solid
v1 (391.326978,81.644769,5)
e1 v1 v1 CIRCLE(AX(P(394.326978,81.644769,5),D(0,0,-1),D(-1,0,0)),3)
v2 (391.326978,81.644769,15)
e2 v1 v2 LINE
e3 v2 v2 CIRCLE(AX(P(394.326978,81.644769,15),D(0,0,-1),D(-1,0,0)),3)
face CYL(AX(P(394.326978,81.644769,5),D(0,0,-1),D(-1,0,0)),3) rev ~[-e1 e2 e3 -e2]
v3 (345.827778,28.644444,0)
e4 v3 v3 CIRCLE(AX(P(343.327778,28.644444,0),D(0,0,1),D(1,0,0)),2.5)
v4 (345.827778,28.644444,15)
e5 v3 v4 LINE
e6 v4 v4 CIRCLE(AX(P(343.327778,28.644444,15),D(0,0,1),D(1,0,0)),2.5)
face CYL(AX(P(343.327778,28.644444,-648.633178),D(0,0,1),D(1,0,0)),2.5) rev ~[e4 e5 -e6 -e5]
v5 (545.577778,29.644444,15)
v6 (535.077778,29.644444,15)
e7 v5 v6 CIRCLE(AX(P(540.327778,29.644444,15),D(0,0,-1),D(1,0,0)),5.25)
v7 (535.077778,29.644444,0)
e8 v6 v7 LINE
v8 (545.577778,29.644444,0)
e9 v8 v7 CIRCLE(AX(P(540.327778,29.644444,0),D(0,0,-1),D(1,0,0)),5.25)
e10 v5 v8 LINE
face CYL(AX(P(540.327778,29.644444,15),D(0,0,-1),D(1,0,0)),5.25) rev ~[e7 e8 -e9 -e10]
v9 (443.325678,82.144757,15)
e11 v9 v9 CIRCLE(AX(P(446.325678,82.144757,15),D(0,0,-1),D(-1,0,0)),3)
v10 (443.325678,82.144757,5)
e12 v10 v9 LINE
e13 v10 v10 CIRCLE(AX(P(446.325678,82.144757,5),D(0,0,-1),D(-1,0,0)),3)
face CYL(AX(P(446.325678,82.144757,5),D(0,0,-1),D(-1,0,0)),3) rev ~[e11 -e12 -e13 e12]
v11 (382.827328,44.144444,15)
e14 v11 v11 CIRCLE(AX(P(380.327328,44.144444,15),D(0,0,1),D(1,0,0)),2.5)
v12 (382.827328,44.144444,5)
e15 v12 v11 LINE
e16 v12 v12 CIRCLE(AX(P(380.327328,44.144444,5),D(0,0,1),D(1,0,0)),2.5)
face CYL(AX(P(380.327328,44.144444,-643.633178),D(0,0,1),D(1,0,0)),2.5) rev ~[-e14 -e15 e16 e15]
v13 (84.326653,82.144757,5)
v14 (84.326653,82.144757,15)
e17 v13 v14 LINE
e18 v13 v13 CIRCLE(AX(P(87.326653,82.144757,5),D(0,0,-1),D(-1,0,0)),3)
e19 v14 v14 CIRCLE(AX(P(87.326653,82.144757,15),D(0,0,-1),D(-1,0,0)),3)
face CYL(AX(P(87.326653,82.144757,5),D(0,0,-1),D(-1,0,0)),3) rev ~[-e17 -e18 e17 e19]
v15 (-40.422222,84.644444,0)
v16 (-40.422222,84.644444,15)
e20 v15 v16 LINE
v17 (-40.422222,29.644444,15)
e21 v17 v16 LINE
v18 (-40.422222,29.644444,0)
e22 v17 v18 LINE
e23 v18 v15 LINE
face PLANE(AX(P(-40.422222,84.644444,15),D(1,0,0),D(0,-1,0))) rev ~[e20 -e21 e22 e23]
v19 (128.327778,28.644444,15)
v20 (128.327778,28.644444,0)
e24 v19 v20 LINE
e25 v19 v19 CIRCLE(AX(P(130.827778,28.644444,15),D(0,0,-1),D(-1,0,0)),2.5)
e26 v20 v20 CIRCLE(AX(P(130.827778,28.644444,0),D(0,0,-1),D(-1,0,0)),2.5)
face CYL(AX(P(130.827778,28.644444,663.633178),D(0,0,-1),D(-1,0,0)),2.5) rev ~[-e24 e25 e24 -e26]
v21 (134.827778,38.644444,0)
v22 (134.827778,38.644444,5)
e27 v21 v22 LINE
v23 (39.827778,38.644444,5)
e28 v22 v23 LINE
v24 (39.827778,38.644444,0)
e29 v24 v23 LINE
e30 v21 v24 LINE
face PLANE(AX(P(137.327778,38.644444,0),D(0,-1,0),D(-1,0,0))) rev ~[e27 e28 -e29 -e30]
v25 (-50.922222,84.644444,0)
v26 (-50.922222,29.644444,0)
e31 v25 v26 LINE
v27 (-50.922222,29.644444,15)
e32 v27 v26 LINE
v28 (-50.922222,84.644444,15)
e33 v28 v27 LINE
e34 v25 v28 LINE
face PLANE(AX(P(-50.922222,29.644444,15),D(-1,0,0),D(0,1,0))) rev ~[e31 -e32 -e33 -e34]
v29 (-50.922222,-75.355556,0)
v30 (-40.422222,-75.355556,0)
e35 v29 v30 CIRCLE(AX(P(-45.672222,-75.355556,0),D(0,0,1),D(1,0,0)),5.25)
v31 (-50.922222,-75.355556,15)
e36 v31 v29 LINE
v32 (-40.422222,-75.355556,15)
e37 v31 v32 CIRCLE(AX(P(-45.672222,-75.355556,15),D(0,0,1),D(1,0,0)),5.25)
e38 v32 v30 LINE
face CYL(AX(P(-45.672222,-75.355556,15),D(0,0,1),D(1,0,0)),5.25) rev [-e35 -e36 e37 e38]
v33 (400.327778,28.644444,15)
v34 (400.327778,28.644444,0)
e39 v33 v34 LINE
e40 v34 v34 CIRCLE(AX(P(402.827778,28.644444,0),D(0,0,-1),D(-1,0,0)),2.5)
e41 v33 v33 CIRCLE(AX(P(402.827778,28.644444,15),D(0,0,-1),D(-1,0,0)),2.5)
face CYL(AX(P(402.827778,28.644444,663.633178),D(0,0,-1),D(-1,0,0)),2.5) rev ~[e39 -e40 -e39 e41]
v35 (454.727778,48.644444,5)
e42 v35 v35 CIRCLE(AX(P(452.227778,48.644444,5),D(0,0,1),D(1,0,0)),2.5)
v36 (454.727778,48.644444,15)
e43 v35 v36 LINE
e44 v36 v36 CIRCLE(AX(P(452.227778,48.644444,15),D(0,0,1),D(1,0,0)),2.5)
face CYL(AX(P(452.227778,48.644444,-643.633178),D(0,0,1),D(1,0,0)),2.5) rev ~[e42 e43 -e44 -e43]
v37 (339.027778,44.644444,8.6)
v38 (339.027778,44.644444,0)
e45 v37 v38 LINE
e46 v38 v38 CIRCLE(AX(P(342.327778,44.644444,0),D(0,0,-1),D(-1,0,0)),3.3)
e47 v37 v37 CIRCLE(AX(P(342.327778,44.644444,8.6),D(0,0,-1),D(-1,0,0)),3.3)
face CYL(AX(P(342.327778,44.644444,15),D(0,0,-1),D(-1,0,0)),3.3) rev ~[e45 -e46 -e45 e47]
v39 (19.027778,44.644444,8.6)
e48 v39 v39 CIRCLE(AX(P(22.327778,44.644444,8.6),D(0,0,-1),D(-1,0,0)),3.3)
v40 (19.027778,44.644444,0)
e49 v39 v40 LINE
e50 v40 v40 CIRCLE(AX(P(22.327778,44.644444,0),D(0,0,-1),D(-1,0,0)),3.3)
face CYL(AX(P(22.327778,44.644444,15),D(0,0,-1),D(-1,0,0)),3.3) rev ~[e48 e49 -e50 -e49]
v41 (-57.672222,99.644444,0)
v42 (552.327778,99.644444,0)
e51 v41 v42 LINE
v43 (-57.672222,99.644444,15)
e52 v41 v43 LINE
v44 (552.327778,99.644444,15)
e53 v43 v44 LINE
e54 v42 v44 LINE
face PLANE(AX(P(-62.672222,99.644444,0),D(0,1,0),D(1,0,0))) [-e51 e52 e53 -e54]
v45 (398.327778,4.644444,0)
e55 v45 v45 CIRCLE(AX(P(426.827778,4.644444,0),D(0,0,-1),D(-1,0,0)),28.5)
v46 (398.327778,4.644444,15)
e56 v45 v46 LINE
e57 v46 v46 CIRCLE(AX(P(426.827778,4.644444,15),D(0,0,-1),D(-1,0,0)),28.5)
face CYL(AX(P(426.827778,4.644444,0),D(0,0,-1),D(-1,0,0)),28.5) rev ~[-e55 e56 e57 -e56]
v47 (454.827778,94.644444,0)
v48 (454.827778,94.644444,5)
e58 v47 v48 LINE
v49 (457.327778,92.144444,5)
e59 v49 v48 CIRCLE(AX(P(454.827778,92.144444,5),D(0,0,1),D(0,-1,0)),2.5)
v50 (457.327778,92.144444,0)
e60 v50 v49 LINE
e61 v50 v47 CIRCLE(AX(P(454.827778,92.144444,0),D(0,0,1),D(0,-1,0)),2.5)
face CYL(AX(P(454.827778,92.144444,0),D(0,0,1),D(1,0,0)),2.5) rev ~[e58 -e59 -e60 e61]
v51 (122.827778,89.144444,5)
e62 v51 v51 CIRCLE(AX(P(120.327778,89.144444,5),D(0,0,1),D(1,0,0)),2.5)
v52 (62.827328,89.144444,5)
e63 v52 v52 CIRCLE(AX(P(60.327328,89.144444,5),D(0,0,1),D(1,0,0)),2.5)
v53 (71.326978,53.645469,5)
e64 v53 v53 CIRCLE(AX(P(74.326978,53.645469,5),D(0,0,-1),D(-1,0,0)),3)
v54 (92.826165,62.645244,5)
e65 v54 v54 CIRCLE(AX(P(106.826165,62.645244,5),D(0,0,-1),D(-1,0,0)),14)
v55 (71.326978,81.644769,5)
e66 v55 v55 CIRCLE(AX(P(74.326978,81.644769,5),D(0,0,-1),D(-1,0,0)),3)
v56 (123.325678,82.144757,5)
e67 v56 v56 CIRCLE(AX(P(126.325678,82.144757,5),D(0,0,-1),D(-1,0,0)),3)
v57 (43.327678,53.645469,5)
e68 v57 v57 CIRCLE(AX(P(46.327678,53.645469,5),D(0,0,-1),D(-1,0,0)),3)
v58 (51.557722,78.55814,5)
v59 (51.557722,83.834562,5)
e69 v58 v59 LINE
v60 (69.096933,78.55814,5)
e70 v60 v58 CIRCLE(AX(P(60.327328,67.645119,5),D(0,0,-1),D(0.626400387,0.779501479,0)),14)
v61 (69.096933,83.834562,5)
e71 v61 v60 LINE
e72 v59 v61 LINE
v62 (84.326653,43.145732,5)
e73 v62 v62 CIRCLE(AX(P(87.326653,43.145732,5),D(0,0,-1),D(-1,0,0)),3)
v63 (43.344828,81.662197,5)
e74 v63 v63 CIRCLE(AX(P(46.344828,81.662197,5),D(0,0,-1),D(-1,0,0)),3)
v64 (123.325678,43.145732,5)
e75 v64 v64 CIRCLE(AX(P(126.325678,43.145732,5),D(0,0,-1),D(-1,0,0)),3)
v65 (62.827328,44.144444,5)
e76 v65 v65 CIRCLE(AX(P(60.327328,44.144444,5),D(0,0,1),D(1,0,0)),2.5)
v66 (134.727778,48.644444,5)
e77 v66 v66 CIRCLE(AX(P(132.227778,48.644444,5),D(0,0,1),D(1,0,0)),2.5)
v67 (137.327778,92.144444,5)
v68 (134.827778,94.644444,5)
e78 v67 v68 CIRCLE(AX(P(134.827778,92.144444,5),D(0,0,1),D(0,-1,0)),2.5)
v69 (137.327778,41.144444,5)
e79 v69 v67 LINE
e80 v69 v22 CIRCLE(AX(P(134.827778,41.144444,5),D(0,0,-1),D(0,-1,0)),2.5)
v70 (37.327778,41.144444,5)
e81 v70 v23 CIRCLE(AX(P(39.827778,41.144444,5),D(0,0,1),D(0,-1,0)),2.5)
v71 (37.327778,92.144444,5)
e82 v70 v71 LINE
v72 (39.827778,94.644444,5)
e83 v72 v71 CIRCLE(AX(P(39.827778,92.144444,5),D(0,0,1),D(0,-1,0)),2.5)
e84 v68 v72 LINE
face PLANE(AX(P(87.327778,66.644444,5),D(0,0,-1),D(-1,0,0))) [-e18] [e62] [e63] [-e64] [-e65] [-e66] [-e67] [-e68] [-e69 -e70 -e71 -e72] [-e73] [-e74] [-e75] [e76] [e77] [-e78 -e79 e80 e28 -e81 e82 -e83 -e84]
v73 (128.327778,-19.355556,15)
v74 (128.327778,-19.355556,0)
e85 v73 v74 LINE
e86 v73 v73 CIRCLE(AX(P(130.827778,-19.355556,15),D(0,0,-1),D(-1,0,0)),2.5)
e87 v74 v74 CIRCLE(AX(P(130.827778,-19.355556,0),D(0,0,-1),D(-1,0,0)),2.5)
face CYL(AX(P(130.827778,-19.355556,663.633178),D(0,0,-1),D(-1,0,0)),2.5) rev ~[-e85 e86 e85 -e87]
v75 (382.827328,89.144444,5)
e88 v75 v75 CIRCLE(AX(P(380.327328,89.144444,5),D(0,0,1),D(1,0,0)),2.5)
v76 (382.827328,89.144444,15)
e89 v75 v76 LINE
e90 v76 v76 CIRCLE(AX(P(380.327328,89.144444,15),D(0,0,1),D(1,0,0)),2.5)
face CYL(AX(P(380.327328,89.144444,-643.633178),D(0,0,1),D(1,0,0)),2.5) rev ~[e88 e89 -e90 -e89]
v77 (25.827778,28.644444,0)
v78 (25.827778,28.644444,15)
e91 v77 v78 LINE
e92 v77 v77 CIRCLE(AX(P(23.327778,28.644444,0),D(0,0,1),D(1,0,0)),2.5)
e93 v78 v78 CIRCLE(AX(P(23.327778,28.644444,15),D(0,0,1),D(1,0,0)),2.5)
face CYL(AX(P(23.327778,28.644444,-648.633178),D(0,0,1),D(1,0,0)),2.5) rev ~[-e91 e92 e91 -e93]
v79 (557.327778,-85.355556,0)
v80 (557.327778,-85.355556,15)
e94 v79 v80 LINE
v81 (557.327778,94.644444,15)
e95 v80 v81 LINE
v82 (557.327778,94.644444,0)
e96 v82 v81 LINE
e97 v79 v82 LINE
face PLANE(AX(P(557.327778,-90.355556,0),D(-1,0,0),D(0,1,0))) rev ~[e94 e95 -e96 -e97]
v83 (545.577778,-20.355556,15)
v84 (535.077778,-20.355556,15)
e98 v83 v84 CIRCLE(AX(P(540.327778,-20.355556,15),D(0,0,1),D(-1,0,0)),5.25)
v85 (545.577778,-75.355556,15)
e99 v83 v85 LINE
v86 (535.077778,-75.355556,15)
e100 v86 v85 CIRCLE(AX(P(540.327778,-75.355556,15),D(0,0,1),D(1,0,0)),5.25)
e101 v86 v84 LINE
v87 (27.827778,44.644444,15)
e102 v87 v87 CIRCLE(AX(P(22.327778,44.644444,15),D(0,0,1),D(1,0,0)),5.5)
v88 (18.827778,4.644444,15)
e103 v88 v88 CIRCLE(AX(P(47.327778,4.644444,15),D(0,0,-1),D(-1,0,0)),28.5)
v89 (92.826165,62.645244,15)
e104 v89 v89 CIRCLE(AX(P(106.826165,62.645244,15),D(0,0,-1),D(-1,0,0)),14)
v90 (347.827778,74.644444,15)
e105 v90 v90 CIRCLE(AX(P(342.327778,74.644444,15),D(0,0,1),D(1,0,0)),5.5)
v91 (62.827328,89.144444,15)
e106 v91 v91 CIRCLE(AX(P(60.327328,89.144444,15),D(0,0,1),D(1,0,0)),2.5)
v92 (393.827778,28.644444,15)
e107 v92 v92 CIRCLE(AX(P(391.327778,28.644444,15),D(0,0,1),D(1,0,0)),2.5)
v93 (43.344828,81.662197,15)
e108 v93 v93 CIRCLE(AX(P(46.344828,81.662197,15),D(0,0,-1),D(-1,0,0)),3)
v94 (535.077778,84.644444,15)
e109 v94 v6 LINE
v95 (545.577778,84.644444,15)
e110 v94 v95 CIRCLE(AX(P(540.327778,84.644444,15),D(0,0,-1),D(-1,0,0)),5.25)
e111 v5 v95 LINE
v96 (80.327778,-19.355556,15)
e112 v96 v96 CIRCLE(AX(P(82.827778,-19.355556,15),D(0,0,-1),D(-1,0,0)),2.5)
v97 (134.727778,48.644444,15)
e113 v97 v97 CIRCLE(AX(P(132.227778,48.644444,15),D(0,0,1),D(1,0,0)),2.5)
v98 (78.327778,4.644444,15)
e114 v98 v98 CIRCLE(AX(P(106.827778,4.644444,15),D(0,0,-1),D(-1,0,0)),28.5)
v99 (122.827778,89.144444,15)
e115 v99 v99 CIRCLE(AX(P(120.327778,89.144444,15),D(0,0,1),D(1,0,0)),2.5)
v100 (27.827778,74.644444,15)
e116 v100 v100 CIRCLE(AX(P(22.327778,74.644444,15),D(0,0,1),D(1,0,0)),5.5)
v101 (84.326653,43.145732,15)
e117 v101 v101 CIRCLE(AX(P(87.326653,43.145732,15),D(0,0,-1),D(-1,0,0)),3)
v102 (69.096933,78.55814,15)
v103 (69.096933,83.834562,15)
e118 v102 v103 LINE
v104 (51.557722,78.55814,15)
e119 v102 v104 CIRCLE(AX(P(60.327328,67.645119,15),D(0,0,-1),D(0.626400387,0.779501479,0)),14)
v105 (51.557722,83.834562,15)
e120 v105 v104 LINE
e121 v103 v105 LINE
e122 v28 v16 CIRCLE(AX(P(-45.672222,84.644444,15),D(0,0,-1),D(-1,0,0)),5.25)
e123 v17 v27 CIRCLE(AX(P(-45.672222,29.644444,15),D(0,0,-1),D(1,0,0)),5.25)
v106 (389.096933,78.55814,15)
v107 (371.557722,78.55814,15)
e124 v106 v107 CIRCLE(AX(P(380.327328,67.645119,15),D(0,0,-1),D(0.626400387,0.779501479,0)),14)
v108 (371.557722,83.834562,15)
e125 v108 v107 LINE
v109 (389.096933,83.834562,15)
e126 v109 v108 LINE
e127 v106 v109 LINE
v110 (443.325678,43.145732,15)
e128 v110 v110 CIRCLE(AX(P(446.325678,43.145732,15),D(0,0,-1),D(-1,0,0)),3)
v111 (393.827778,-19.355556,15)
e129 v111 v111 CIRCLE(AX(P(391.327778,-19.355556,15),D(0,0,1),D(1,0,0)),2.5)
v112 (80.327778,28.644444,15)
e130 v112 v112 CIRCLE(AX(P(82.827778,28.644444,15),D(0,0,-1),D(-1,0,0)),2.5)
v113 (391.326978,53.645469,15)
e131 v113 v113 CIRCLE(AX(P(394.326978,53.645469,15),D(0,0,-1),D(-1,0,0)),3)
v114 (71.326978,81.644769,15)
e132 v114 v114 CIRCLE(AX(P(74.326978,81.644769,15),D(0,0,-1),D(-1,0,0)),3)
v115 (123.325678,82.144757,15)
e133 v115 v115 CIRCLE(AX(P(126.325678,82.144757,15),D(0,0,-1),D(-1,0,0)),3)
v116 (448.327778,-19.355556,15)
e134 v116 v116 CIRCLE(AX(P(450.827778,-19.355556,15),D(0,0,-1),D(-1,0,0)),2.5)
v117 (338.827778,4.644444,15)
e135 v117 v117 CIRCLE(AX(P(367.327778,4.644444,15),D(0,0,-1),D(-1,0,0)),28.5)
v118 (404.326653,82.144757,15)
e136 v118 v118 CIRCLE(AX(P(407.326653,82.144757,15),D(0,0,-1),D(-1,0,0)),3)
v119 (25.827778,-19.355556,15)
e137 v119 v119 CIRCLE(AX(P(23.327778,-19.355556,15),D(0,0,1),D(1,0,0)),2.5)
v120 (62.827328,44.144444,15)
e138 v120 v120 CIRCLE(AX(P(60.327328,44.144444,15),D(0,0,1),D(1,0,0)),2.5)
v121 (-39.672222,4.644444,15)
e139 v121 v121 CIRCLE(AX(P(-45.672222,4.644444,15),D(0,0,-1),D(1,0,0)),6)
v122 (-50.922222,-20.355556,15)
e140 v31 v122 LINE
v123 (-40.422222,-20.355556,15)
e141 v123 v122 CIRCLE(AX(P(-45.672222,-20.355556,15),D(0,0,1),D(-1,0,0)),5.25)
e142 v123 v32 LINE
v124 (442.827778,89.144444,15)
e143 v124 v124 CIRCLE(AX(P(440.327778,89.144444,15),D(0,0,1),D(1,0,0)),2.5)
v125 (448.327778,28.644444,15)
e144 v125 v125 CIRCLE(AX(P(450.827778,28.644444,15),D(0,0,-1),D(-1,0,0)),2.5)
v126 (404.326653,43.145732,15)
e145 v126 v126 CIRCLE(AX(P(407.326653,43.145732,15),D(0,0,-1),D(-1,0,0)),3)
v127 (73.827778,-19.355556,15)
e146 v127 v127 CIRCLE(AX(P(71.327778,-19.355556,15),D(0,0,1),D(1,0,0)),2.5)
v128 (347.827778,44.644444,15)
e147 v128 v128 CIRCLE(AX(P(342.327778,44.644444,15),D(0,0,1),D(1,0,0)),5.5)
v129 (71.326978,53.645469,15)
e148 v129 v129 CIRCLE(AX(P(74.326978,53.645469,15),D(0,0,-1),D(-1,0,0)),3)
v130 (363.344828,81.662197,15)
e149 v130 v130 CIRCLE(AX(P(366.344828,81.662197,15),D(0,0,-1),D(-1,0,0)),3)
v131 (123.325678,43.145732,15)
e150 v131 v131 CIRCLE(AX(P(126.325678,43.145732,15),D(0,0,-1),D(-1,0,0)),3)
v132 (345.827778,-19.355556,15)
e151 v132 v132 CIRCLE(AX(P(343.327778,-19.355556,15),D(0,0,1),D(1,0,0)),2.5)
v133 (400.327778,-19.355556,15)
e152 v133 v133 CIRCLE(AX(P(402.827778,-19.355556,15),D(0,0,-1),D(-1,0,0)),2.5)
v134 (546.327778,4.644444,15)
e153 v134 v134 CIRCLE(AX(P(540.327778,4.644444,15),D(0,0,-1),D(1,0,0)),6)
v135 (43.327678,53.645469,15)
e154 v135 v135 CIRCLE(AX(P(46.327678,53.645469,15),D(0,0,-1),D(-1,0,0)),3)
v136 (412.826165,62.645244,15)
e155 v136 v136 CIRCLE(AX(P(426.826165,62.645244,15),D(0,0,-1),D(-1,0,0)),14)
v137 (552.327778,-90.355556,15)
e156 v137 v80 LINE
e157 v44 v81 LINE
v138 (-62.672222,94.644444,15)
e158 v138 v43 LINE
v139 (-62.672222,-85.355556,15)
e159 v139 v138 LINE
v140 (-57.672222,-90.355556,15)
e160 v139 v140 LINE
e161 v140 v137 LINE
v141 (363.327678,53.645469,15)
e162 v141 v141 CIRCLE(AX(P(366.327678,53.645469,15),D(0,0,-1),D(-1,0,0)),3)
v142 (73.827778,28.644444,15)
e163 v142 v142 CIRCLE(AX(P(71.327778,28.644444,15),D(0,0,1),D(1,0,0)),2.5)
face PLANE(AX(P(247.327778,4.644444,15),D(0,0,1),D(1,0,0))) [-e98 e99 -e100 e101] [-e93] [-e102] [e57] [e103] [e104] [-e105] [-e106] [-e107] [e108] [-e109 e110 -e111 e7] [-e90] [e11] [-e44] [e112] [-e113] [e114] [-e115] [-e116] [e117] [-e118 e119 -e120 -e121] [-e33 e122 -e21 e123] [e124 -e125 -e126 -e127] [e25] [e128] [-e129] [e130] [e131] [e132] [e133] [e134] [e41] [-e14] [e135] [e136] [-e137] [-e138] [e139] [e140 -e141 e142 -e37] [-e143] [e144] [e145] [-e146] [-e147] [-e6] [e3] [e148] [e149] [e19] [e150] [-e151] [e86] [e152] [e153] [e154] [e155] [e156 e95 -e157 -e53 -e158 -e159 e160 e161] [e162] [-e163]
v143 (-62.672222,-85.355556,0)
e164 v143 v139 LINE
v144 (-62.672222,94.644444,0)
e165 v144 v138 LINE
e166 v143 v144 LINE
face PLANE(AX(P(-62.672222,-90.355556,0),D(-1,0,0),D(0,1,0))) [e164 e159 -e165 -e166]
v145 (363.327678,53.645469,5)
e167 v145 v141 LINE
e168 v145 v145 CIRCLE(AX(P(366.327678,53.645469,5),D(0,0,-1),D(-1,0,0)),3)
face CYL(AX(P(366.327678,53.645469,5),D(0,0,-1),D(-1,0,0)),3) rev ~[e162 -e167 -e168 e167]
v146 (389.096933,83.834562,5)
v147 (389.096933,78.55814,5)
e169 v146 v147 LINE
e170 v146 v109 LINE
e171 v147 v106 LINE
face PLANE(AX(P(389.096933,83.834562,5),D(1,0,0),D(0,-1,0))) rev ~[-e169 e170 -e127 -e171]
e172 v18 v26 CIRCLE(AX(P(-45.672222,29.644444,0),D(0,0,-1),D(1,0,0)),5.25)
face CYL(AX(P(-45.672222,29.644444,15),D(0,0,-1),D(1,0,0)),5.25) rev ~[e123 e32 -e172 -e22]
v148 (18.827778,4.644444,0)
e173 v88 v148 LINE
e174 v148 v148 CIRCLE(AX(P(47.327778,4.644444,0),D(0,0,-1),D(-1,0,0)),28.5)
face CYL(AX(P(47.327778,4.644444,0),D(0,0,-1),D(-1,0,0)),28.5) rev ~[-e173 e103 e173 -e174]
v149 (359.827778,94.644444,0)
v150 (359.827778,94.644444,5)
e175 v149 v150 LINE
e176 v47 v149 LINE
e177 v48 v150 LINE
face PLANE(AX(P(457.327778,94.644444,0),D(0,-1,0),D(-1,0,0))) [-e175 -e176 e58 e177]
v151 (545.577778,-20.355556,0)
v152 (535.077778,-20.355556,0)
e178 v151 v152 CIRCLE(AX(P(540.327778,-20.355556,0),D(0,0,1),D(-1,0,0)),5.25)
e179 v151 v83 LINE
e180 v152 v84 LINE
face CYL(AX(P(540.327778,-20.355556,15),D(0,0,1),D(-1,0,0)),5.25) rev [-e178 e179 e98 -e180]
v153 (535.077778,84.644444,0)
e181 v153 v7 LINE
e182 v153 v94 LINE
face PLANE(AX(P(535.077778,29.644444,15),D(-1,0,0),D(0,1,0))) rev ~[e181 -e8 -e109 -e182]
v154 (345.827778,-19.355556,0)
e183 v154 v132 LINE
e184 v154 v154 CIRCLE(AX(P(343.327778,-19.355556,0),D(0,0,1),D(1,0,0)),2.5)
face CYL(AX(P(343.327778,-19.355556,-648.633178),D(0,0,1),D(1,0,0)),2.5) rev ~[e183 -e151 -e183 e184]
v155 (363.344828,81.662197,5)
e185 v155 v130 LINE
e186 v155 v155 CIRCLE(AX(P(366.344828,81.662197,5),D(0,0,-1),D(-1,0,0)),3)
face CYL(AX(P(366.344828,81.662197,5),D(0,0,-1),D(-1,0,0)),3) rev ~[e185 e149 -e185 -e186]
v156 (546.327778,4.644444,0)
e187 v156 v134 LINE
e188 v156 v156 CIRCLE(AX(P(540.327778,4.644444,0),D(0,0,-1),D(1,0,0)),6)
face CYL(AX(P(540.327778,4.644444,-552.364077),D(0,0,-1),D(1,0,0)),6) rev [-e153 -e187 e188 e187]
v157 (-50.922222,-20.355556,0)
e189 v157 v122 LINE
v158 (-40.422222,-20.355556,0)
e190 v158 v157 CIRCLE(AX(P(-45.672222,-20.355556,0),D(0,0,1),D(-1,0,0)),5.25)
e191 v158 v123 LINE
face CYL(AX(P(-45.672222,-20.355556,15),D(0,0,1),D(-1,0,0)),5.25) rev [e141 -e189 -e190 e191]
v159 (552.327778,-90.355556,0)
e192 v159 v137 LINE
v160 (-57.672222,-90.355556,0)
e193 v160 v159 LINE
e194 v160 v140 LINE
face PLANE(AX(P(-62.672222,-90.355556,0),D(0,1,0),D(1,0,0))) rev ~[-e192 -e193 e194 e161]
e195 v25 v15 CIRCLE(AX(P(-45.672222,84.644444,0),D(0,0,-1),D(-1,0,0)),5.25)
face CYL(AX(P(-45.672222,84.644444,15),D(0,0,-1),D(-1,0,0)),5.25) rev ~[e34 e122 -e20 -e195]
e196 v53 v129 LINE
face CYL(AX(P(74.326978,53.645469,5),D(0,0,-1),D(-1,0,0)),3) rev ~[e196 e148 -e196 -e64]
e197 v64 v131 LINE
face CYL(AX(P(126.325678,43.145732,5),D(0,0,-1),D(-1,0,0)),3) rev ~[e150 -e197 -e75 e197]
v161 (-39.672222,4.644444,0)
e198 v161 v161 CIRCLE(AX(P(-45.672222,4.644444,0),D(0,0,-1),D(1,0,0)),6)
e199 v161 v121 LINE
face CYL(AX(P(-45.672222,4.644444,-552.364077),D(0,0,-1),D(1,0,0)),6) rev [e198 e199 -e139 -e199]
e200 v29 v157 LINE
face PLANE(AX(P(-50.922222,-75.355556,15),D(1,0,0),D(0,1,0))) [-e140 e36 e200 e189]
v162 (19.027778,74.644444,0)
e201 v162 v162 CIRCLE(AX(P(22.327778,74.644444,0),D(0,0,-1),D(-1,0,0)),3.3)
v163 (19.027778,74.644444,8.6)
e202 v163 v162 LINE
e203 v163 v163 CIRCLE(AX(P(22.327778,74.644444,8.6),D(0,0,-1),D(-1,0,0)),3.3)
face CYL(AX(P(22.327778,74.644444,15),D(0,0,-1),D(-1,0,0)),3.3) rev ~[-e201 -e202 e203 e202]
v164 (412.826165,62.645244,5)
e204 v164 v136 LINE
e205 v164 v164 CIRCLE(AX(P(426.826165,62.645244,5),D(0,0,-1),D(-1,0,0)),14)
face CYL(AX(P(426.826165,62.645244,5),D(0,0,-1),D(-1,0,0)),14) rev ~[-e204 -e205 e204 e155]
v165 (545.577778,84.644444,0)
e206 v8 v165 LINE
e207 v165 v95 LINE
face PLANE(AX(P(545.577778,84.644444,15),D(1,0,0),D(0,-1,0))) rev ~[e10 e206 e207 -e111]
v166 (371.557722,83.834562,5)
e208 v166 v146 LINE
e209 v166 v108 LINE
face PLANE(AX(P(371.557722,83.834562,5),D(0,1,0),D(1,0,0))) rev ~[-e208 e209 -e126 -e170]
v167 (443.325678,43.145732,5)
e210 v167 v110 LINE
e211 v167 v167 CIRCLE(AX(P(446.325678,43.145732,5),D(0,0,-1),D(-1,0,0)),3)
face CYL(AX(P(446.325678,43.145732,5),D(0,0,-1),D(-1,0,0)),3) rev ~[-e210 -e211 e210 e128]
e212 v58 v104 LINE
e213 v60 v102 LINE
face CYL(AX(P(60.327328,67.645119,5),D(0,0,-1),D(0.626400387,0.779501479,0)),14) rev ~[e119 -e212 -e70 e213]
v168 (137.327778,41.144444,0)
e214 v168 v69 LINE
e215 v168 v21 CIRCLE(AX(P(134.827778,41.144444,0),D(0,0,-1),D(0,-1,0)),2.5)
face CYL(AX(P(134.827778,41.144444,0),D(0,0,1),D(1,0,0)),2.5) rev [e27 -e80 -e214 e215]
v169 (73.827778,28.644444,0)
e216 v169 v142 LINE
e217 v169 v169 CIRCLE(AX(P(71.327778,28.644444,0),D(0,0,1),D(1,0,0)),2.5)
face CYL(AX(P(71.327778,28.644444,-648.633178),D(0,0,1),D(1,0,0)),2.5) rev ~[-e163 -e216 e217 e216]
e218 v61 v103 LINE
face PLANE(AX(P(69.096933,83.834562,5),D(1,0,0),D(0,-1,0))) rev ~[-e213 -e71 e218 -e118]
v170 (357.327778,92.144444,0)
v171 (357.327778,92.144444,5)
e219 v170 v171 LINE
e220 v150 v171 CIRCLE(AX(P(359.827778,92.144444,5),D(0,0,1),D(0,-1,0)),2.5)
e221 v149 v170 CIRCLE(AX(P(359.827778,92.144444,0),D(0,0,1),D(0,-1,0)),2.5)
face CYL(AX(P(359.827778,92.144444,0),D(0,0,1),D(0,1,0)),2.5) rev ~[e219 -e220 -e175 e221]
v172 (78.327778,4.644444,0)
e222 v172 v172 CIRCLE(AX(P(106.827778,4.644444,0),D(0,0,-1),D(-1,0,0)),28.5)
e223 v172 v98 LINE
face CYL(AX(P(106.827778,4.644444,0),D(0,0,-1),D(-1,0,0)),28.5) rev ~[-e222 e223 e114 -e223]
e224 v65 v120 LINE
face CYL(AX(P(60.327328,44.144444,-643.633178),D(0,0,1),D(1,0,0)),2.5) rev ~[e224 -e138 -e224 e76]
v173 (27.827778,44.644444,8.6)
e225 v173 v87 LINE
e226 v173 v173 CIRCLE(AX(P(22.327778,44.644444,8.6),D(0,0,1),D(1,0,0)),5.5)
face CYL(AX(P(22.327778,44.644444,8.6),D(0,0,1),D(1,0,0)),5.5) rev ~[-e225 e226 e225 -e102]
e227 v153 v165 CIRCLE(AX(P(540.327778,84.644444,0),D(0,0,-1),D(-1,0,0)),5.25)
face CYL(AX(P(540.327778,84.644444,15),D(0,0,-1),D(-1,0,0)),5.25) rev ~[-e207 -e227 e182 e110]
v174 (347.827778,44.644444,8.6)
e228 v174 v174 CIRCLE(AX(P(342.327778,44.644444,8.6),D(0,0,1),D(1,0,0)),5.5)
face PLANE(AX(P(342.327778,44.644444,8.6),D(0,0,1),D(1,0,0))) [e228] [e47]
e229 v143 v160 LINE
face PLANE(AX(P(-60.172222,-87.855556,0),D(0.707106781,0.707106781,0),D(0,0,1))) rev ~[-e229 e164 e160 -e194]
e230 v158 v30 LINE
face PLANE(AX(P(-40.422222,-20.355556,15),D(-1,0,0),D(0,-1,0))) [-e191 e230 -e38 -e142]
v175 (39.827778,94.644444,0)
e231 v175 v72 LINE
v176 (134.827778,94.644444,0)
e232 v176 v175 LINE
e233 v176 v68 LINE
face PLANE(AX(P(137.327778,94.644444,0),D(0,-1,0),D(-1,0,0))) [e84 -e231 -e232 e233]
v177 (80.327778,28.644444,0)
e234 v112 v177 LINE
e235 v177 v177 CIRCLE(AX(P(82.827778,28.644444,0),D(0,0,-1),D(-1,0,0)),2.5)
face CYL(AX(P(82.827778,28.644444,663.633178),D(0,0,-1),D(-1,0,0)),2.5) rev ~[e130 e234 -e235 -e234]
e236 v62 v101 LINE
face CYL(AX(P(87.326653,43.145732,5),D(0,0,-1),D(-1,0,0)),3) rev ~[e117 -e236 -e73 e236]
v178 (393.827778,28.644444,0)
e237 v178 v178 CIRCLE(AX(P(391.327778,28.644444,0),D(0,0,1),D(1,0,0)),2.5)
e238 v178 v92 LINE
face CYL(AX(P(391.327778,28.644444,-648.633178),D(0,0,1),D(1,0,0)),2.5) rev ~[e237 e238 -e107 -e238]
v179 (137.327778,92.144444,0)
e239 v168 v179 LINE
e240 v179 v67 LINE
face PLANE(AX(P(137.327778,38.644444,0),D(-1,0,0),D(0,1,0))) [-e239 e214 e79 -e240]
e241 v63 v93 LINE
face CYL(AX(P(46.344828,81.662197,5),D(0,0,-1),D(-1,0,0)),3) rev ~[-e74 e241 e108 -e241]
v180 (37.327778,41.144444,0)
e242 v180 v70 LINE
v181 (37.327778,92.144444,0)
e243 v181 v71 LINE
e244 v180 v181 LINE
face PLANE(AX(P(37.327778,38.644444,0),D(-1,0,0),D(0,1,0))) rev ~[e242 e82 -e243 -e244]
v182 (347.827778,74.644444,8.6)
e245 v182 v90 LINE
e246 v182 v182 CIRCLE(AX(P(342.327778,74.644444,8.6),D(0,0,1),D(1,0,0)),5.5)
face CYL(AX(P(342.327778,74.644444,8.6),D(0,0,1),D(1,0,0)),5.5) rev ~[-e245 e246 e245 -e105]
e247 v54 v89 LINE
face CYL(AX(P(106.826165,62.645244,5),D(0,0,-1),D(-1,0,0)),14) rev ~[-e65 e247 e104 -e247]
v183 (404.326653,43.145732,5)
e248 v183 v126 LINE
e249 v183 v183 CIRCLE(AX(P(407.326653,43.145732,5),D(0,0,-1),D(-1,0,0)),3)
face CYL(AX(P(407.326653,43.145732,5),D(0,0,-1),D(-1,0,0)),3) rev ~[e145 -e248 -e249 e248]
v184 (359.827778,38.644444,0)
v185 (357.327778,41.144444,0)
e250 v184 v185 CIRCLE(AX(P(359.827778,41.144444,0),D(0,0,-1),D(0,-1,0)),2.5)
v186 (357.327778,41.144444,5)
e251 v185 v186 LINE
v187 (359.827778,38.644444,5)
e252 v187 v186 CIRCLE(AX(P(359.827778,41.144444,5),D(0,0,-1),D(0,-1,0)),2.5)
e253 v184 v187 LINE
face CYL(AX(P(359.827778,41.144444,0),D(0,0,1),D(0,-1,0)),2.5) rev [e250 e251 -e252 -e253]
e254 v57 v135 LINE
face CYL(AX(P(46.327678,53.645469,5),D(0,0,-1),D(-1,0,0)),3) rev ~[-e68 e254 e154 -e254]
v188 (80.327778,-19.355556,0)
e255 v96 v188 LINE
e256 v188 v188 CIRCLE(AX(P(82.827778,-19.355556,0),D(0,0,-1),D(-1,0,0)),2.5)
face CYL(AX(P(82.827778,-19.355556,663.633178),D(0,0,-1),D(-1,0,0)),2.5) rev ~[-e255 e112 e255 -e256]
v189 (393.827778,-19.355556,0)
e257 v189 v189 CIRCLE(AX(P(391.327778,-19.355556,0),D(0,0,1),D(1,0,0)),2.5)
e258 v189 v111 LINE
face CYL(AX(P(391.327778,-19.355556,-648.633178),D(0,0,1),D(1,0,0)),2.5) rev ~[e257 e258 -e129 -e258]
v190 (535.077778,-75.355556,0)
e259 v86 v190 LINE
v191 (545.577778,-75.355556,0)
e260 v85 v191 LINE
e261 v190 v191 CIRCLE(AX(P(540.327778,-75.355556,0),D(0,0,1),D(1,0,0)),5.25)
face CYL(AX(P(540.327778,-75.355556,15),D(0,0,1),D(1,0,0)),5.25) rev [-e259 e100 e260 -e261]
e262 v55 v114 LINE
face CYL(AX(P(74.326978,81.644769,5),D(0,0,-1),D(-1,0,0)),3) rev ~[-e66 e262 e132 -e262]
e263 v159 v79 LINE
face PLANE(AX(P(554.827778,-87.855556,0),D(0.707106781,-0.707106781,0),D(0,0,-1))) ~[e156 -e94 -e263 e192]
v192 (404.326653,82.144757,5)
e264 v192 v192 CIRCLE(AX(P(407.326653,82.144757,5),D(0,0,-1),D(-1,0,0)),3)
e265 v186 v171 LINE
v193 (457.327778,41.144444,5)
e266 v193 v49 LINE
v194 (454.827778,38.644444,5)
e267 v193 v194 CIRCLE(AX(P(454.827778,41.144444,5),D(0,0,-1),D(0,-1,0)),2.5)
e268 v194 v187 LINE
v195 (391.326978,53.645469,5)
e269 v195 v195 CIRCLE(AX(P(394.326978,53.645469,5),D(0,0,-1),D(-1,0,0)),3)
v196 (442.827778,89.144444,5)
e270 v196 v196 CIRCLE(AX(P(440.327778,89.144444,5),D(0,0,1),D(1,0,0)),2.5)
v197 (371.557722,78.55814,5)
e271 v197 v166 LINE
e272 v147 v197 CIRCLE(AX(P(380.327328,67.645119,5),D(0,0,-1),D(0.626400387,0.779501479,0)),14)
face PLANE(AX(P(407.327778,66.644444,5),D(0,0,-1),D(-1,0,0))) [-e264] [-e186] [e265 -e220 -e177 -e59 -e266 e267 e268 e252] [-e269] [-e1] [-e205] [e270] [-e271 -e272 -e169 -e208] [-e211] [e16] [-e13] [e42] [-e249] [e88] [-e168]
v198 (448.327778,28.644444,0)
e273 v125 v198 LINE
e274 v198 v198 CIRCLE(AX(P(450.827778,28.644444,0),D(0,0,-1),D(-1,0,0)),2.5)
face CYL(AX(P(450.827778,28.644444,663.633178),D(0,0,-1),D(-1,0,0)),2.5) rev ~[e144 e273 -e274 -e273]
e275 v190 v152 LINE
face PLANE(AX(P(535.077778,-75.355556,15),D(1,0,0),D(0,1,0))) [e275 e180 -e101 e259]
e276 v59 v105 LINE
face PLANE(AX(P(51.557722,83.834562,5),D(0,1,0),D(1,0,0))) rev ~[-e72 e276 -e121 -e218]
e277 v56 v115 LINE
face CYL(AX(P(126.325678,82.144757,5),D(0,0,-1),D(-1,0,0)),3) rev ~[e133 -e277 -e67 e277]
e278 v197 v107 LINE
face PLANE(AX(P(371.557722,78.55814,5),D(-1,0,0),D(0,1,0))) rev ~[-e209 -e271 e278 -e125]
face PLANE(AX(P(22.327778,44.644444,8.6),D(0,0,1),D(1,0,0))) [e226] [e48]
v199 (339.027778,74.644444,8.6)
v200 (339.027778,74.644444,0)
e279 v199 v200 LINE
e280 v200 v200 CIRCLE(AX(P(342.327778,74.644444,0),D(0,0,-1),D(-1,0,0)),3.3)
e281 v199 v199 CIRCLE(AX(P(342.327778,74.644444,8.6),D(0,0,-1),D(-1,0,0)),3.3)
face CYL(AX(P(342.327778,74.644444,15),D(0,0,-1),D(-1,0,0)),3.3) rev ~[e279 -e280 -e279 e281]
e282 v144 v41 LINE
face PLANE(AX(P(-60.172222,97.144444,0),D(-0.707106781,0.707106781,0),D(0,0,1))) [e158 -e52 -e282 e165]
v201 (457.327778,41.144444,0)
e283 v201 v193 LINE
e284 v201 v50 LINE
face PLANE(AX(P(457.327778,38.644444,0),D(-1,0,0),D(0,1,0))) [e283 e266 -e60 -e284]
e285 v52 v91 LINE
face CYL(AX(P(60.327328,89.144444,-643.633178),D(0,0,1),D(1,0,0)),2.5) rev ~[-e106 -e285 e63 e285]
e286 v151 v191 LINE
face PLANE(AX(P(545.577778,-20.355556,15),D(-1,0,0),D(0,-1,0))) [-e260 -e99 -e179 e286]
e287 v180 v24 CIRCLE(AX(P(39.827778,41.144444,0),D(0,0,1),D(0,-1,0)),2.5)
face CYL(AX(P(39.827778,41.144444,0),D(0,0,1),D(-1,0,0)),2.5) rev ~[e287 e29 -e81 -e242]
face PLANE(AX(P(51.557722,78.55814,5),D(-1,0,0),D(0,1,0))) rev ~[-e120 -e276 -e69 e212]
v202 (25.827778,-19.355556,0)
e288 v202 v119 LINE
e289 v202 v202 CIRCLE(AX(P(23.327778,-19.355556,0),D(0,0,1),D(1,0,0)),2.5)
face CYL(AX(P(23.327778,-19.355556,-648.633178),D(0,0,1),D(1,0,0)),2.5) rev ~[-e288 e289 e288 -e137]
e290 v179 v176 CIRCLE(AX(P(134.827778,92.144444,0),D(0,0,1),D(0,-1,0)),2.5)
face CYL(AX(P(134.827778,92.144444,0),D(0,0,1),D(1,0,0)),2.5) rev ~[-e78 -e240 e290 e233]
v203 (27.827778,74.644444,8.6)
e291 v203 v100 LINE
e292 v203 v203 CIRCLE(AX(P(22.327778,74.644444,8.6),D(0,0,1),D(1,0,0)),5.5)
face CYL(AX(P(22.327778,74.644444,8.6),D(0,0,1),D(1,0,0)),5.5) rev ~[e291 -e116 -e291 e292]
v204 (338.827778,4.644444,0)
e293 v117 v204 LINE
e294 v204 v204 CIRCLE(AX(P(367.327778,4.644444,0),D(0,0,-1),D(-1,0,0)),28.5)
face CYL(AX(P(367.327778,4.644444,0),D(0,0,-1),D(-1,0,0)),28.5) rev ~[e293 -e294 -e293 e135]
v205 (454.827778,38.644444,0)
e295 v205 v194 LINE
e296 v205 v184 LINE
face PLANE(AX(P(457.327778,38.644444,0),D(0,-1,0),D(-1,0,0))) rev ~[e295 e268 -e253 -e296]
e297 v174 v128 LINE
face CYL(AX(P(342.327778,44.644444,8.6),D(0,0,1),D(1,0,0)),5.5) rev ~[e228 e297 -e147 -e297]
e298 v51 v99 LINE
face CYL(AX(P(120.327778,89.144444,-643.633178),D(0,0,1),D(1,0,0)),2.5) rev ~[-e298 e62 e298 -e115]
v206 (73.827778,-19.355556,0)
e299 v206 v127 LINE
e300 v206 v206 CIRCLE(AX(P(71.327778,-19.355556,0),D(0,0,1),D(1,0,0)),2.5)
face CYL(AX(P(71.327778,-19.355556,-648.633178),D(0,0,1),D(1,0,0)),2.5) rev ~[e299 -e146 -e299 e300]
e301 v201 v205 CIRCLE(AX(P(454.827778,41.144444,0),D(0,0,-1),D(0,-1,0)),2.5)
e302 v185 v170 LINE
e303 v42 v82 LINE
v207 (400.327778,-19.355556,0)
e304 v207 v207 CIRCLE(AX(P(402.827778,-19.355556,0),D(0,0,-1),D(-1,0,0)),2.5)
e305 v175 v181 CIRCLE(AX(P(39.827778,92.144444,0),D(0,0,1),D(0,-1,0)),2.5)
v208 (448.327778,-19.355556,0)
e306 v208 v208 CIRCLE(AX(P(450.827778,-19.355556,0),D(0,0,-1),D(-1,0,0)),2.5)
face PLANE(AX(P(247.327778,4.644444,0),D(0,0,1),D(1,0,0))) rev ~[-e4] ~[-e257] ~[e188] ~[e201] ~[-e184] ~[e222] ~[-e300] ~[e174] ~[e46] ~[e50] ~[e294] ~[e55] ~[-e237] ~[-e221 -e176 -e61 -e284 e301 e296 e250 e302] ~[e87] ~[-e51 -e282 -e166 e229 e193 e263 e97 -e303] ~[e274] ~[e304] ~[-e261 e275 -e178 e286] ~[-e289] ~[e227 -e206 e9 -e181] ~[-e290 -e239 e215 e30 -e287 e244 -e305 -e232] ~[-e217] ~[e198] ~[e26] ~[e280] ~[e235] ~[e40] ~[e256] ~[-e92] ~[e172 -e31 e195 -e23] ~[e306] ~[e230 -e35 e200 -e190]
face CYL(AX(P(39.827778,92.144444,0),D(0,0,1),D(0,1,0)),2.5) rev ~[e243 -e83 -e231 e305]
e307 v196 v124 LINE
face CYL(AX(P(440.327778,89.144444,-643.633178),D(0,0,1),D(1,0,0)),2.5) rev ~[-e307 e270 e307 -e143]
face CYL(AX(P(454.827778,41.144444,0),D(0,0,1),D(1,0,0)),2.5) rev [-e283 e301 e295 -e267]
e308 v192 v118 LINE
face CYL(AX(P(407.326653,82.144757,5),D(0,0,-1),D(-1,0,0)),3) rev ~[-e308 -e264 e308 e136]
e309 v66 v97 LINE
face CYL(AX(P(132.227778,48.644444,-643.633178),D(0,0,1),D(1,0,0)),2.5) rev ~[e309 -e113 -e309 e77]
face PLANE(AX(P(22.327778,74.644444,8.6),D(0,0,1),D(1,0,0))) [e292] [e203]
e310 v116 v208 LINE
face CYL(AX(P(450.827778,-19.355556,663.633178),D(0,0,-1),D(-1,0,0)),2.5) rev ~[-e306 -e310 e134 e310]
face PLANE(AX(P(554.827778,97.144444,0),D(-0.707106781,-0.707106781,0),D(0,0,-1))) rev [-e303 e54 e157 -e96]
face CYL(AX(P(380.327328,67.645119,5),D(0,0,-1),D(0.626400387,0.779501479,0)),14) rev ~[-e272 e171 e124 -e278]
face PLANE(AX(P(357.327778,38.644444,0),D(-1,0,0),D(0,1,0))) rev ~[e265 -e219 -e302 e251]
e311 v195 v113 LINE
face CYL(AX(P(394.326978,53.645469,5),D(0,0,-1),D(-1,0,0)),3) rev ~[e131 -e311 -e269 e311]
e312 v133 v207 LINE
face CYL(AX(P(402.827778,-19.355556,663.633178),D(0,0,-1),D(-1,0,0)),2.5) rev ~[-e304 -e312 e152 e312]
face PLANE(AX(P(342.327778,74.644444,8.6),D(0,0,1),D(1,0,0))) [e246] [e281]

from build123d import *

# Parameters (mm, degrees)
SKETCH1_W                                           = 620
SKETCH1_H                                           = 190
BOSS_EXTRUDE1_DEPTH                                 = 15
CUT_EXTRUDE1_DEPTH                                  = 567.364076537
CUT_EXTRUDE1_DEPTH_BACK                             = 567.364076537
SKETCH2_R                                           = 6
CUT_EXTRUDE2_DEPTH                                  = 567.364076537
LPATTERN1_COUNT                                     = 2
LPATTERN1_PITCH                                     = 586
CHAMFER1_SIZE                                       = 5
SKETCH6_W                                           = 100
SKETCH6_H                                           = 56
CUT_EXTRUDE3_DEPTH                                  = 5
FILLET1_R                                           = 2.5
SKETCH7_R                                           = 14
SKETCH7_R_2                                         = 3
CUT_EXTRUDE4_DEPTH                                  = 567.25371274
M6_TAPPED_HOLE1_D                                   = 5
M6_TAPPED_HOLE2_D                                   = 5
SKETCH12_R                                          = 28.5
CUT_EXTRUDE5_DEPTH                                  = 567.364076537
SKETCH13_R                                          = 28.5
CUT_EXTRUDE6_DEPTH                                  = 567.364076537
M6_TAPPED_HOLE3_D                                   = 5
LPATTERN5_COUNT                                     = 2
LPATTERN5_PITCH                                     = 320
FILLET1_OF_LPATTERN5_R                              = 2.5
CBORE_FOR_M6_HEX_SOCKET_HEAD_CAP_SCREW1_D           = 6.6
CBORE_FOR_M6_HEX_SOCKET_HEAD_CAP_SCREW1_CBORE_D     = 11
CBORE_FOR_M6_HEX_SOCKET_HEAD_CAP_SCREW1_CBORE_DEPTH = 6.4


with BuildPart() as part:
    # Sketch1 → Boss-Extrude1 (new body)
    with BuildSketch(Plane.XY):
        with Locations((247.327777778, 4.644444444)):
            Rectangle(SKETCH1_W, SKETCH1_H)
    extrude(amount=BOSS_EXTRUDE1_DEPTH)

    # Sketch2 → Cut-Extrude1 (cut, two sides: drawn at the far end of the back side and taken through both)
    with BuildSketch(Plane.XY.offset(15).offset(-CUT_EXTRUDE1_DEPTH_BACK)):
        with Locations((-45.672222222, 4.644444444)):
            Circle(SKETCH2_R)
        with Locations((540.327777778, 4.644444444)):
            Circle(SKETCH2_R)
    extrude(amount=CUT_EXTRUDE1_DEPTH + CUT_EXTRUDE1_DEPTH_BACK, mode=Mode.SUBTRACT)

    # Sketch5 → Cut-Extrude2 (cut, symmetric)
    with BuildSketch(Plane.XY.offset(15)):
        with BuildLine():
            Line((-40.422222222, 84.644444444), (-40.422222222, 29.644444444))
            ThreePointArc((-40.422222222, 29.644444444), (-45.672222222, 24.394444444), (-50.922222222, 29.644444444))
            Line((-50.922222222, 29.644444444), (-50.922222222, 84.644444444))
            ThreePointArc((-50.922222222, 84.644444444), (-45.672222222, 89.894444444), (-40.422222222, 84.644444444))
        make_face()
        with BuildLine():
            Line((-40.422222222, -20.355555556), (-40.422222222, -75.355555556))
            ThreePointArc((-40.422222222, -75.355555556), (-45.672222222, -80.605555556), (-50.922222222, -75.355555556))
            Line((-50.922222222, -75.355555556), (-50.922222222, -20.355555556))
            ThreePointArc((-50.922222222, -20.355555556), (-45.672222222, -15.105555556), (-40.422222222, -20.355555556))
        make_face()
    cut_extrude2 = extrude(amount=CUT_EXTRUDE2_DEPTH, both=True, mode=Mode.SUBTRACT)

    # LPattern1: Cut-Extrude2 ×2
    with Locations(*[(i * LPATTERN1_PITCH, 0, 0) for i in range(1, LPATTERN1_COUNT)]):
        add(cut_extrude2, mode=Mode.SUBTRACT)

    # Chamfer1
    chamfer1_edges = [part.edges().sort_by_distance(p)[0] for p in [
        (-62.672222222, 99.644444444, 7.5),
        (557.327777778, 99.644444444, 7.5),
        (557.327777778, -90.355555556, 7.5),
        (-62.672222222, -90.355555556, 7.5),
    ]]
    chamfer(chamfer1_edges, length=CHAMFER1_SIZE)

    # Sketch6 → Cut-Extrude3 (cut)
    with BuildSketch(Plane(origin=(0, 0, 0), x_dir=(-1, 0, 0), z_dir=(0, 0, -1))):
        with Locations((-87.327777778, 66.644444444)):
            Rectangle(SKETCH6_W, SKETCH6_H)
    cut_extrude3 = extrude(amount=-CUT_EXTRUDE3_DEPTH, mode=Mode.SUBTRACT)

    # Fillet1
    fillet1_edges = [part.edges().sort_by_distance(p)[0] for p in [
        (137.327777778, 38.644444444, 2.5),
        (137.327777778, 94.644444444, 2.5),
        (37.327777778, 94.644444444, 2.5),
        (37.327777778, 38.644444444, 2.5),
    ]]
    fillet(fillet1_edges, radius=FILLET1_R)

    # Sketch7 → Cut-Extrude4 (cut, through all)
    with BuildSketch(Plane(origin=(0, 0, 5), x_dir=(-1, 0, 0), z_dir=(0, 0, -1))):
        with Locations((-106.826165278, 62.645244444)):
            Circle(SKETCH7_R)
        with Locations((-46.34482821, 81.662196851)):
            Circle(SKETCH7_R_2)
        with Locations((-46.327677778, 53.645469444)):
            Circle(SKETCH7_R_2)
        with Locations((-74.326977778, 53.645469444)):
            Circle(SKETCH7_R_2)
        with Locations((-74.326977778, 81.644769444)):
            Circle(SKETCH7_R_2)
        with Locations((-87.326652778, 82.144756944)):
            Circle(SKETCH7_R_2)
        with Locations((-87.326652778, 43.145731944)):
            Circle(SKETCH7_R_2)
        with Locations((-126.325677778, 43.145731944)):
            Circle(SKETCH7_R_2)
        with Locations((-126.325677778, 82.144756944)):
            Circle(SKETCH7_R_2)
        with BuildLine():
            Line((-51.557722364, 83.834562358), (-69.096933191, 83.834562358))
            Line((-69.096933191, 83.834562358), (-69.096933191, 78.558140149))
            ThreePointArc((-69.096933191, 78.558140149), (-60.327327778, 53.645119444), (-51.557722364, 78.558140149))
            Line((-51.557722364, 78.558140149), (-51.557722364, 83.834562358))
        make_face()
    cut_extrude4 = extrude(amount=-CUT_EXTRUDE4_DEPTH, mode=Mode.SUBTRACT)

    # M6 Tapped Hole1 (through all)
    with Locations(Plane(origin=(0, 0, 5), x_dir=(-1, 0, 0), z_dir=(0, 0, -1))):
        with Locations((-60.327327778, 44.144444444), (-60.327327778, 89.144444444), (-132.227777778, 48.644444444), (-120.327777778, 89.144444444)):
            m6_tapped_hole1 = Hole(M6_TAPPED_HOLE1_D / 2)

    # M6 Tapped Hole2 (through all)
    with Locations(Plane.XY.offset(15)):
        with Locations((82.827777778, -19.355555556), (82.827777778, 28.644444444), (130.827777778, -19.355555556), (130.827777778, 28.644444444)):
            m6_tapped_hole2 = Hole(M6_TAPPED_HOLE2_D / 2)

    # Sketch12 → Cut-Extrude5 (cut, through all)
    with BuildSketch(Plane(origin=(0, 0, 0), x_dir=(-1, 0, 0), z_dir=(0, 0, -1))):
        with Locations((-106.827777778, 4.644444444)):
            Circle(SKETCH12_R)
    cut_extrude5 = extrude(amount=-CUT_EXTRUDE5_DEPTH, mode=Mode.SUBTRACT)

    # Sketch13 → Cut-Extrude6 (cut, symmetric)
    with BuildSketch(Plane(origin=(0, 0, 0), x_dir=(-1, 0, 0), z_dir=(0, 0, -1))):
        with Locations((-47.327777778, 4.644444444)):
            Circle(SKETCH13_R)
    cut_extrude6 = extrude(amount=CUT_EXTRUDE6_DEPTH, both=True, mode=Mode.SUBTRACT)

    # M6 Tapped Hole3 (through all)
    with Locations(Plane(origin=(0, 0, 0), x_dir=(-1, 0, 0), z_dir=(0, 0, -1))):
        with Locations((-23.327777778, -19.355555556), (-71.327777778, -19.355555556), (-23.327777778, 28.644444444), (-71.327777778, 28.644444444)):
            m6_tapped_hole3 = Hole(M6_TAPPED_HOLE3_D / 2)

    # LPattern5: Cut-Extrude3, Cut-Extrude4, M6 Tapped Hole1, M6 Tapped Hole2, Cut-Extrude5, Cut-Extrude6, M6 Tapped Hole3 ×2
    with Locations(*[(i * LPATTERN5_PITCH, 0, 0) for i in range(1, LPATTERN5_COUNT)]):
        add(cut_extrude3, mode=Mode.SUBTRACT)
        add(cut_extrude4, mode=Mode.SUBTRACT)
        add(m6_tapped_hole1, mode=Mode.SUBTRACT)
        add(m6_tapped_hole2, mode=Mode.SUBTRACT)
        add(cut_extrude5, mode=Mode.SUBTRACT)
        add(cut_extrude6, mode=Mode.SUBTRACT)
        add(m6_tapped_hole3, mode=Mode.SUBTRACT)

    # Fillet1 of LPattern5
    fillet1_of_lpattern5_edges = [part.edges().sort_by_distance(p)[0] for p in [
        (457.327777778, 38.644444444, 2.5),
        (457.327777778, 94.644444444, 2.5),
        (357.327777778, 94.644444444, 2.5),
        (357.327777778, 38.644444444, 2.5),
    ]]
    fillet(fillet1_of_lpattern5_edges, radius=FILLET1_OF_LPATTERN5_R)

    # CBORE for M6 Hex Socket Head Cap Screw1 (through all)
    with Locations(Plane.XY.offset(15)):
        with Locations((342.327777778, 44.644444444), (342.327777778, 74.644444444), (22.327777778, 44.644444444), (22.327777778, 74.644444444)):
            CounterBoreHole(CBORE_FOR_M6_HEX_SOCKET_HEAD_CAP_SCREW1_D / 2, CBORE_FOR_M6_HEX_SOCKET_HEAD_CAP_SCREW1_CBORE_D / 2, CBORE_FOR_M6_HEX_SOCKET_HEAD_CAP_SCREW1_CBORE_DEPTH)


solid = part.part
